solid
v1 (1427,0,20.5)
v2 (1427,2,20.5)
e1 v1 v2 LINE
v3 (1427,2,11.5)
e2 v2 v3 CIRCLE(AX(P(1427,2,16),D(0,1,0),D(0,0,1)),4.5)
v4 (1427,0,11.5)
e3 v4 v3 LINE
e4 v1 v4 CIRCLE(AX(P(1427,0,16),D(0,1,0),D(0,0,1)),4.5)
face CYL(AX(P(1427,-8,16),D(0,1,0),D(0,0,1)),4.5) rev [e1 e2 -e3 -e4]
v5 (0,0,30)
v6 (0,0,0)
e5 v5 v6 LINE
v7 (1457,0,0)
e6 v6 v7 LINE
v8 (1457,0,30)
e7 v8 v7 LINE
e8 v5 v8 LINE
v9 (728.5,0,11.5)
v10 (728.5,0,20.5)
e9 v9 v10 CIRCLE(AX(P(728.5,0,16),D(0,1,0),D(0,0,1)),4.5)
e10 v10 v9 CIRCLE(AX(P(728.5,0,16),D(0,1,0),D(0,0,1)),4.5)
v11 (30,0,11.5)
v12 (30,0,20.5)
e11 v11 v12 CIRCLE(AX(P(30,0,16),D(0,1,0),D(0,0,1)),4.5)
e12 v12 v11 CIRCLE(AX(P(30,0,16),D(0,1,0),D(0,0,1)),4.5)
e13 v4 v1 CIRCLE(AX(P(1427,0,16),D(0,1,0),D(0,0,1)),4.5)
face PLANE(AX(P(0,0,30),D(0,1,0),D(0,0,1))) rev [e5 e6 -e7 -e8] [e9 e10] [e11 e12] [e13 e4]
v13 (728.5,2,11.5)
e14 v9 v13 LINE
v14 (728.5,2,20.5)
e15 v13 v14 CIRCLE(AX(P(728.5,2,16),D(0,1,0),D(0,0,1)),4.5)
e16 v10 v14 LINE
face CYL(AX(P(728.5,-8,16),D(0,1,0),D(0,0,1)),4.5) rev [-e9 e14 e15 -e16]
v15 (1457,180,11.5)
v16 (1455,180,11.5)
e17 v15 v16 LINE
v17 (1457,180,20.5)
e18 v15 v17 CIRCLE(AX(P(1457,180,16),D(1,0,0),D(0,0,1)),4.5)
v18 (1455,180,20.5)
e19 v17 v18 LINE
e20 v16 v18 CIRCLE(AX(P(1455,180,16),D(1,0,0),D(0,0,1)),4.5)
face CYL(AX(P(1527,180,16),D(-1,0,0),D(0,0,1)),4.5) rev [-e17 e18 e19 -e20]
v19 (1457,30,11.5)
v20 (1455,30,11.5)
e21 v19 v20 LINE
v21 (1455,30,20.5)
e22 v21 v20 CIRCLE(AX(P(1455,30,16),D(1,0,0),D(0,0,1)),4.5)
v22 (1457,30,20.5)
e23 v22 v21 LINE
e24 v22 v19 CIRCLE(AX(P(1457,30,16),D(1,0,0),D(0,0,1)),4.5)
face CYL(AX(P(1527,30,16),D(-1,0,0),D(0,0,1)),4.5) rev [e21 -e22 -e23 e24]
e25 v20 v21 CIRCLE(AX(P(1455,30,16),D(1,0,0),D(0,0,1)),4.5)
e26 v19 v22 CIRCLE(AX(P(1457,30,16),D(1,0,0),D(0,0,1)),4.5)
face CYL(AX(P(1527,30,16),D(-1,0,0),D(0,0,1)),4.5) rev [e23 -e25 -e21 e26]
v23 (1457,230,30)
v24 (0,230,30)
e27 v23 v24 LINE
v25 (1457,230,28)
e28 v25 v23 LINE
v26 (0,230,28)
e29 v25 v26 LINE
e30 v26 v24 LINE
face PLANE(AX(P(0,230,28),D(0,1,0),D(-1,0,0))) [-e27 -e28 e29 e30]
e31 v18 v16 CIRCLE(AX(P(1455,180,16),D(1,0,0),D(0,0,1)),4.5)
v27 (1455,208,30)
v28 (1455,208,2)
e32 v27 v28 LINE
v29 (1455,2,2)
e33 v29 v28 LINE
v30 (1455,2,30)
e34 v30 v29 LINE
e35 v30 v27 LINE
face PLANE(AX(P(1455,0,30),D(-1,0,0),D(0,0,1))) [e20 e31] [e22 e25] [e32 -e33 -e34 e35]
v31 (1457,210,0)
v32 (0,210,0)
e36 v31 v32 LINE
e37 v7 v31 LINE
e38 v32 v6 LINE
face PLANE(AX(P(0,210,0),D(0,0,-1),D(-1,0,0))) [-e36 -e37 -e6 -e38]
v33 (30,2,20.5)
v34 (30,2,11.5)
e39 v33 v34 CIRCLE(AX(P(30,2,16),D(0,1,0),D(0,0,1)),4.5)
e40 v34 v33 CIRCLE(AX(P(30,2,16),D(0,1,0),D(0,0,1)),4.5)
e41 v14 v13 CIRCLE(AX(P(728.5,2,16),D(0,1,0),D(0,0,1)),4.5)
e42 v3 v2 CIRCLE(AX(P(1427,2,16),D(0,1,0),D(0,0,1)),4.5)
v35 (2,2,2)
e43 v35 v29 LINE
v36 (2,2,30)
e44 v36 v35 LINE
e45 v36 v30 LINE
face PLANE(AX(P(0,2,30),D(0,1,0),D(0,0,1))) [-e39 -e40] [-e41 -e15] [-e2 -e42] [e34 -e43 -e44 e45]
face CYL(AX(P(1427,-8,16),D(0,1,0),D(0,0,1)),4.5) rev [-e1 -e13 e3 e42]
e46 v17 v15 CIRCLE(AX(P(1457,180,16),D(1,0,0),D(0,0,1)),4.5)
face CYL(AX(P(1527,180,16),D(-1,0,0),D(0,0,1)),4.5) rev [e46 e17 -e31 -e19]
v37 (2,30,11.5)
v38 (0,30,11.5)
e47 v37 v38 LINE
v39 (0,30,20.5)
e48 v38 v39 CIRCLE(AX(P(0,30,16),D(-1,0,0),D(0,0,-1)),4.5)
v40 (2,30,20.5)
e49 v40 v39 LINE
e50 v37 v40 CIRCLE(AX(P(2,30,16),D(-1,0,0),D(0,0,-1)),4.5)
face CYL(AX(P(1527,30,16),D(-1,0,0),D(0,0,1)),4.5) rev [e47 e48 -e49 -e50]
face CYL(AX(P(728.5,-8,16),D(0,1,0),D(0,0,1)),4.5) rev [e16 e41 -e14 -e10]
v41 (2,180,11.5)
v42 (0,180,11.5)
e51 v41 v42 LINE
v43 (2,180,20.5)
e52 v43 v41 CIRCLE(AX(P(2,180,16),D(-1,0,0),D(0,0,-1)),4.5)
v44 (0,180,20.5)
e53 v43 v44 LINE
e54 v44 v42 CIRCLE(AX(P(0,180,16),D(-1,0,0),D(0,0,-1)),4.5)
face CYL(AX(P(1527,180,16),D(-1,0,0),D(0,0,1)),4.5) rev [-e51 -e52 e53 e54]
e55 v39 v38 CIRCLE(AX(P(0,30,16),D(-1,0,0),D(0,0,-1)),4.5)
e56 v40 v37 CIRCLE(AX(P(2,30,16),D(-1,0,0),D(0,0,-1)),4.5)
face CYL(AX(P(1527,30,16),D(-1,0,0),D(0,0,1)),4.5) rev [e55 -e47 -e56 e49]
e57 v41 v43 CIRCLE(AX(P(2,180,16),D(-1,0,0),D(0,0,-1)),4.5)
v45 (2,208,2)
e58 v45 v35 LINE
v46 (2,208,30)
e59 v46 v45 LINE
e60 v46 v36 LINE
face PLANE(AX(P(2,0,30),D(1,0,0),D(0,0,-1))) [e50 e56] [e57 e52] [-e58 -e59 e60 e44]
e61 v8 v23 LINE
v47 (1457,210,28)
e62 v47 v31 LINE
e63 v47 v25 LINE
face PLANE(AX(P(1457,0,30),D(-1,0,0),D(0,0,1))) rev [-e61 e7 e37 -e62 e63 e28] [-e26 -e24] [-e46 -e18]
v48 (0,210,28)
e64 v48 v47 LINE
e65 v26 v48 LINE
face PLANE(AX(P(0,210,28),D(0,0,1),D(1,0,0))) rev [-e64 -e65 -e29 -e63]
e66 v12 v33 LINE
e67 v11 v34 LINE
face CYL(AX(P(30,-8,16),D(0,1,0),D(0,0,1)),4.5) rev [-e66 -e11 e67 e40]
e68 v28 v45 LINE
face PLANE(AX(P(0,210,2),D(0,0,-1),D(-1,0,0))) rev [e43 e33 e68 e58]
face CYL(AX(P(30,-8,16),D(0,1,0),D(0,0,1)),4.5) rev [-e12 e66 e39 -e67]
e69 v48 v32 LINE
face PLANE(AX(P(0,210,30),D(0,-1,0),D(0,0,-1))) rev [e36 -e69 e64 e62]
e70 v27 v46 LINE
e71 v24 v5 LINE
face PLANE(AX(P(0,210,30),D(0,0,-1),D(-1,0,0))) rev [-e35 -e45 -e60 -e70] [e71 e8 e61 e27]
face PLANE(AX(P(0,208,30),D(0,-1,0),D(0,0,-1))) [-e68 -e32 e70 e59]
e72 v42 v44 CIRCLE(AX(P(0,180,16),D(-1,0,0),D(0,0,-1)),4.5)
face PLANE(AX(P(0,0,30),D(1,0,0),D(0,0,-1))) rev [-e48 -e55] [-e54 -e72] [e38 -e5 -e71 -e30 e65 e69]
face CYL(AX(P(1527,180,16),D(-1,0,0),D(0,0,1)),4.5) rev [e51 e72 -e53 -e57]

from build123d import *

# Parameters (mm, degrees)
SKETCH_1_W               = 1457
SKETCH_1_H               = 210
EXTRUDE_1_DEPTH          = 30
SHELL_1_T                = -2
SKETCH_2_W               = 1457
SKETCH_2_H               = 20
EXTRUDE_2_DEPTH          = 2
SKETCH_3_R               = 4.5
CUT_EXTRUDE_1_DEPTH      = 10
CUT_EXTRUDE_2_DEPTH      = 1525
CUT_EXTRUDE_2_DEPTH_BACK = 76
SKETCH_4_R               = 4.5


with BuildPart() as part:
    # 草图1 → 凸台-拉伸1 (new body)
    with BuildSketch(Plane.XY):
        with Locations((728.5, 105)):
            Rectangle(SKETCH_1_W, SKETCH_1_H)
    extrude(amount=EXTRUDE_1_DEPTH)

    # 抽壳1
    shell_1_openings = [part.faces().sort_by_distance(p)[0] for p in [
        (728.5, 105, 30),
    ]]
    offset(amount=SHELL_1_T, openings=shell_1_openings, kind=Kind.INTERSECTION)

    # 草图2 → 凸台-拉伸2 (add)
    with BuildSketch(Plane.XY.offset(30)):
        with Locations((728.5, 220)):
            Rectangle(SKETCH_2_W, SKETCH_2_H)
    extrude(amount=-EXTRUDE_2_DEPTH)

    # 草图3 → 切除-拉伸1 (cut)
    with BuildSketch(Plane(origin=(0, 2, 0), x_dir=(1, 0, 0), z_dir=(0, 1, 0))):
        with Locations(Location((1427, -16, 0), (0, 0, 270))):
            Circle(SKETCH_3_R)
        with Locations(Location((728.5, -16, 0), (0, 0, 270))):
            Circle(SKETCH_3_R)
        with Locations(Location((30, -16, 0), (0, 0, 270))):
            Circle(SKETCH_3_R)
    extrude(amount=-CUT_EXTRUDE_1_DEPTH, mode=Mode.SUBTRACT)

    # 草图4 → 切除-拉伸2 (cut, two sides: drawn at the far end of the back side and taken through both)
    with BuildSketch(Plane(origin=(2, 0, 0), x_dir=(0, 0, -1), z_dir=(1, 0, 0)).offset(-CUT_EXTRUDE_2_DEPTH_BACK)):
        with Locations(Location((-16, 30, 0), (0, 0, 180))):
            Circle(SKETCH_4_R)
        with Locations(Location((-16, 180, 0), (0, 0, 180))):
            Circle(SKETCH_4_R)
    extrude(amount=CUT_EXTRUDE_2_DEPTH + CUT_EXTRUDE_2_DEPTH_BACK, mode=Mode.SUBTRACT)


solid = part.part
